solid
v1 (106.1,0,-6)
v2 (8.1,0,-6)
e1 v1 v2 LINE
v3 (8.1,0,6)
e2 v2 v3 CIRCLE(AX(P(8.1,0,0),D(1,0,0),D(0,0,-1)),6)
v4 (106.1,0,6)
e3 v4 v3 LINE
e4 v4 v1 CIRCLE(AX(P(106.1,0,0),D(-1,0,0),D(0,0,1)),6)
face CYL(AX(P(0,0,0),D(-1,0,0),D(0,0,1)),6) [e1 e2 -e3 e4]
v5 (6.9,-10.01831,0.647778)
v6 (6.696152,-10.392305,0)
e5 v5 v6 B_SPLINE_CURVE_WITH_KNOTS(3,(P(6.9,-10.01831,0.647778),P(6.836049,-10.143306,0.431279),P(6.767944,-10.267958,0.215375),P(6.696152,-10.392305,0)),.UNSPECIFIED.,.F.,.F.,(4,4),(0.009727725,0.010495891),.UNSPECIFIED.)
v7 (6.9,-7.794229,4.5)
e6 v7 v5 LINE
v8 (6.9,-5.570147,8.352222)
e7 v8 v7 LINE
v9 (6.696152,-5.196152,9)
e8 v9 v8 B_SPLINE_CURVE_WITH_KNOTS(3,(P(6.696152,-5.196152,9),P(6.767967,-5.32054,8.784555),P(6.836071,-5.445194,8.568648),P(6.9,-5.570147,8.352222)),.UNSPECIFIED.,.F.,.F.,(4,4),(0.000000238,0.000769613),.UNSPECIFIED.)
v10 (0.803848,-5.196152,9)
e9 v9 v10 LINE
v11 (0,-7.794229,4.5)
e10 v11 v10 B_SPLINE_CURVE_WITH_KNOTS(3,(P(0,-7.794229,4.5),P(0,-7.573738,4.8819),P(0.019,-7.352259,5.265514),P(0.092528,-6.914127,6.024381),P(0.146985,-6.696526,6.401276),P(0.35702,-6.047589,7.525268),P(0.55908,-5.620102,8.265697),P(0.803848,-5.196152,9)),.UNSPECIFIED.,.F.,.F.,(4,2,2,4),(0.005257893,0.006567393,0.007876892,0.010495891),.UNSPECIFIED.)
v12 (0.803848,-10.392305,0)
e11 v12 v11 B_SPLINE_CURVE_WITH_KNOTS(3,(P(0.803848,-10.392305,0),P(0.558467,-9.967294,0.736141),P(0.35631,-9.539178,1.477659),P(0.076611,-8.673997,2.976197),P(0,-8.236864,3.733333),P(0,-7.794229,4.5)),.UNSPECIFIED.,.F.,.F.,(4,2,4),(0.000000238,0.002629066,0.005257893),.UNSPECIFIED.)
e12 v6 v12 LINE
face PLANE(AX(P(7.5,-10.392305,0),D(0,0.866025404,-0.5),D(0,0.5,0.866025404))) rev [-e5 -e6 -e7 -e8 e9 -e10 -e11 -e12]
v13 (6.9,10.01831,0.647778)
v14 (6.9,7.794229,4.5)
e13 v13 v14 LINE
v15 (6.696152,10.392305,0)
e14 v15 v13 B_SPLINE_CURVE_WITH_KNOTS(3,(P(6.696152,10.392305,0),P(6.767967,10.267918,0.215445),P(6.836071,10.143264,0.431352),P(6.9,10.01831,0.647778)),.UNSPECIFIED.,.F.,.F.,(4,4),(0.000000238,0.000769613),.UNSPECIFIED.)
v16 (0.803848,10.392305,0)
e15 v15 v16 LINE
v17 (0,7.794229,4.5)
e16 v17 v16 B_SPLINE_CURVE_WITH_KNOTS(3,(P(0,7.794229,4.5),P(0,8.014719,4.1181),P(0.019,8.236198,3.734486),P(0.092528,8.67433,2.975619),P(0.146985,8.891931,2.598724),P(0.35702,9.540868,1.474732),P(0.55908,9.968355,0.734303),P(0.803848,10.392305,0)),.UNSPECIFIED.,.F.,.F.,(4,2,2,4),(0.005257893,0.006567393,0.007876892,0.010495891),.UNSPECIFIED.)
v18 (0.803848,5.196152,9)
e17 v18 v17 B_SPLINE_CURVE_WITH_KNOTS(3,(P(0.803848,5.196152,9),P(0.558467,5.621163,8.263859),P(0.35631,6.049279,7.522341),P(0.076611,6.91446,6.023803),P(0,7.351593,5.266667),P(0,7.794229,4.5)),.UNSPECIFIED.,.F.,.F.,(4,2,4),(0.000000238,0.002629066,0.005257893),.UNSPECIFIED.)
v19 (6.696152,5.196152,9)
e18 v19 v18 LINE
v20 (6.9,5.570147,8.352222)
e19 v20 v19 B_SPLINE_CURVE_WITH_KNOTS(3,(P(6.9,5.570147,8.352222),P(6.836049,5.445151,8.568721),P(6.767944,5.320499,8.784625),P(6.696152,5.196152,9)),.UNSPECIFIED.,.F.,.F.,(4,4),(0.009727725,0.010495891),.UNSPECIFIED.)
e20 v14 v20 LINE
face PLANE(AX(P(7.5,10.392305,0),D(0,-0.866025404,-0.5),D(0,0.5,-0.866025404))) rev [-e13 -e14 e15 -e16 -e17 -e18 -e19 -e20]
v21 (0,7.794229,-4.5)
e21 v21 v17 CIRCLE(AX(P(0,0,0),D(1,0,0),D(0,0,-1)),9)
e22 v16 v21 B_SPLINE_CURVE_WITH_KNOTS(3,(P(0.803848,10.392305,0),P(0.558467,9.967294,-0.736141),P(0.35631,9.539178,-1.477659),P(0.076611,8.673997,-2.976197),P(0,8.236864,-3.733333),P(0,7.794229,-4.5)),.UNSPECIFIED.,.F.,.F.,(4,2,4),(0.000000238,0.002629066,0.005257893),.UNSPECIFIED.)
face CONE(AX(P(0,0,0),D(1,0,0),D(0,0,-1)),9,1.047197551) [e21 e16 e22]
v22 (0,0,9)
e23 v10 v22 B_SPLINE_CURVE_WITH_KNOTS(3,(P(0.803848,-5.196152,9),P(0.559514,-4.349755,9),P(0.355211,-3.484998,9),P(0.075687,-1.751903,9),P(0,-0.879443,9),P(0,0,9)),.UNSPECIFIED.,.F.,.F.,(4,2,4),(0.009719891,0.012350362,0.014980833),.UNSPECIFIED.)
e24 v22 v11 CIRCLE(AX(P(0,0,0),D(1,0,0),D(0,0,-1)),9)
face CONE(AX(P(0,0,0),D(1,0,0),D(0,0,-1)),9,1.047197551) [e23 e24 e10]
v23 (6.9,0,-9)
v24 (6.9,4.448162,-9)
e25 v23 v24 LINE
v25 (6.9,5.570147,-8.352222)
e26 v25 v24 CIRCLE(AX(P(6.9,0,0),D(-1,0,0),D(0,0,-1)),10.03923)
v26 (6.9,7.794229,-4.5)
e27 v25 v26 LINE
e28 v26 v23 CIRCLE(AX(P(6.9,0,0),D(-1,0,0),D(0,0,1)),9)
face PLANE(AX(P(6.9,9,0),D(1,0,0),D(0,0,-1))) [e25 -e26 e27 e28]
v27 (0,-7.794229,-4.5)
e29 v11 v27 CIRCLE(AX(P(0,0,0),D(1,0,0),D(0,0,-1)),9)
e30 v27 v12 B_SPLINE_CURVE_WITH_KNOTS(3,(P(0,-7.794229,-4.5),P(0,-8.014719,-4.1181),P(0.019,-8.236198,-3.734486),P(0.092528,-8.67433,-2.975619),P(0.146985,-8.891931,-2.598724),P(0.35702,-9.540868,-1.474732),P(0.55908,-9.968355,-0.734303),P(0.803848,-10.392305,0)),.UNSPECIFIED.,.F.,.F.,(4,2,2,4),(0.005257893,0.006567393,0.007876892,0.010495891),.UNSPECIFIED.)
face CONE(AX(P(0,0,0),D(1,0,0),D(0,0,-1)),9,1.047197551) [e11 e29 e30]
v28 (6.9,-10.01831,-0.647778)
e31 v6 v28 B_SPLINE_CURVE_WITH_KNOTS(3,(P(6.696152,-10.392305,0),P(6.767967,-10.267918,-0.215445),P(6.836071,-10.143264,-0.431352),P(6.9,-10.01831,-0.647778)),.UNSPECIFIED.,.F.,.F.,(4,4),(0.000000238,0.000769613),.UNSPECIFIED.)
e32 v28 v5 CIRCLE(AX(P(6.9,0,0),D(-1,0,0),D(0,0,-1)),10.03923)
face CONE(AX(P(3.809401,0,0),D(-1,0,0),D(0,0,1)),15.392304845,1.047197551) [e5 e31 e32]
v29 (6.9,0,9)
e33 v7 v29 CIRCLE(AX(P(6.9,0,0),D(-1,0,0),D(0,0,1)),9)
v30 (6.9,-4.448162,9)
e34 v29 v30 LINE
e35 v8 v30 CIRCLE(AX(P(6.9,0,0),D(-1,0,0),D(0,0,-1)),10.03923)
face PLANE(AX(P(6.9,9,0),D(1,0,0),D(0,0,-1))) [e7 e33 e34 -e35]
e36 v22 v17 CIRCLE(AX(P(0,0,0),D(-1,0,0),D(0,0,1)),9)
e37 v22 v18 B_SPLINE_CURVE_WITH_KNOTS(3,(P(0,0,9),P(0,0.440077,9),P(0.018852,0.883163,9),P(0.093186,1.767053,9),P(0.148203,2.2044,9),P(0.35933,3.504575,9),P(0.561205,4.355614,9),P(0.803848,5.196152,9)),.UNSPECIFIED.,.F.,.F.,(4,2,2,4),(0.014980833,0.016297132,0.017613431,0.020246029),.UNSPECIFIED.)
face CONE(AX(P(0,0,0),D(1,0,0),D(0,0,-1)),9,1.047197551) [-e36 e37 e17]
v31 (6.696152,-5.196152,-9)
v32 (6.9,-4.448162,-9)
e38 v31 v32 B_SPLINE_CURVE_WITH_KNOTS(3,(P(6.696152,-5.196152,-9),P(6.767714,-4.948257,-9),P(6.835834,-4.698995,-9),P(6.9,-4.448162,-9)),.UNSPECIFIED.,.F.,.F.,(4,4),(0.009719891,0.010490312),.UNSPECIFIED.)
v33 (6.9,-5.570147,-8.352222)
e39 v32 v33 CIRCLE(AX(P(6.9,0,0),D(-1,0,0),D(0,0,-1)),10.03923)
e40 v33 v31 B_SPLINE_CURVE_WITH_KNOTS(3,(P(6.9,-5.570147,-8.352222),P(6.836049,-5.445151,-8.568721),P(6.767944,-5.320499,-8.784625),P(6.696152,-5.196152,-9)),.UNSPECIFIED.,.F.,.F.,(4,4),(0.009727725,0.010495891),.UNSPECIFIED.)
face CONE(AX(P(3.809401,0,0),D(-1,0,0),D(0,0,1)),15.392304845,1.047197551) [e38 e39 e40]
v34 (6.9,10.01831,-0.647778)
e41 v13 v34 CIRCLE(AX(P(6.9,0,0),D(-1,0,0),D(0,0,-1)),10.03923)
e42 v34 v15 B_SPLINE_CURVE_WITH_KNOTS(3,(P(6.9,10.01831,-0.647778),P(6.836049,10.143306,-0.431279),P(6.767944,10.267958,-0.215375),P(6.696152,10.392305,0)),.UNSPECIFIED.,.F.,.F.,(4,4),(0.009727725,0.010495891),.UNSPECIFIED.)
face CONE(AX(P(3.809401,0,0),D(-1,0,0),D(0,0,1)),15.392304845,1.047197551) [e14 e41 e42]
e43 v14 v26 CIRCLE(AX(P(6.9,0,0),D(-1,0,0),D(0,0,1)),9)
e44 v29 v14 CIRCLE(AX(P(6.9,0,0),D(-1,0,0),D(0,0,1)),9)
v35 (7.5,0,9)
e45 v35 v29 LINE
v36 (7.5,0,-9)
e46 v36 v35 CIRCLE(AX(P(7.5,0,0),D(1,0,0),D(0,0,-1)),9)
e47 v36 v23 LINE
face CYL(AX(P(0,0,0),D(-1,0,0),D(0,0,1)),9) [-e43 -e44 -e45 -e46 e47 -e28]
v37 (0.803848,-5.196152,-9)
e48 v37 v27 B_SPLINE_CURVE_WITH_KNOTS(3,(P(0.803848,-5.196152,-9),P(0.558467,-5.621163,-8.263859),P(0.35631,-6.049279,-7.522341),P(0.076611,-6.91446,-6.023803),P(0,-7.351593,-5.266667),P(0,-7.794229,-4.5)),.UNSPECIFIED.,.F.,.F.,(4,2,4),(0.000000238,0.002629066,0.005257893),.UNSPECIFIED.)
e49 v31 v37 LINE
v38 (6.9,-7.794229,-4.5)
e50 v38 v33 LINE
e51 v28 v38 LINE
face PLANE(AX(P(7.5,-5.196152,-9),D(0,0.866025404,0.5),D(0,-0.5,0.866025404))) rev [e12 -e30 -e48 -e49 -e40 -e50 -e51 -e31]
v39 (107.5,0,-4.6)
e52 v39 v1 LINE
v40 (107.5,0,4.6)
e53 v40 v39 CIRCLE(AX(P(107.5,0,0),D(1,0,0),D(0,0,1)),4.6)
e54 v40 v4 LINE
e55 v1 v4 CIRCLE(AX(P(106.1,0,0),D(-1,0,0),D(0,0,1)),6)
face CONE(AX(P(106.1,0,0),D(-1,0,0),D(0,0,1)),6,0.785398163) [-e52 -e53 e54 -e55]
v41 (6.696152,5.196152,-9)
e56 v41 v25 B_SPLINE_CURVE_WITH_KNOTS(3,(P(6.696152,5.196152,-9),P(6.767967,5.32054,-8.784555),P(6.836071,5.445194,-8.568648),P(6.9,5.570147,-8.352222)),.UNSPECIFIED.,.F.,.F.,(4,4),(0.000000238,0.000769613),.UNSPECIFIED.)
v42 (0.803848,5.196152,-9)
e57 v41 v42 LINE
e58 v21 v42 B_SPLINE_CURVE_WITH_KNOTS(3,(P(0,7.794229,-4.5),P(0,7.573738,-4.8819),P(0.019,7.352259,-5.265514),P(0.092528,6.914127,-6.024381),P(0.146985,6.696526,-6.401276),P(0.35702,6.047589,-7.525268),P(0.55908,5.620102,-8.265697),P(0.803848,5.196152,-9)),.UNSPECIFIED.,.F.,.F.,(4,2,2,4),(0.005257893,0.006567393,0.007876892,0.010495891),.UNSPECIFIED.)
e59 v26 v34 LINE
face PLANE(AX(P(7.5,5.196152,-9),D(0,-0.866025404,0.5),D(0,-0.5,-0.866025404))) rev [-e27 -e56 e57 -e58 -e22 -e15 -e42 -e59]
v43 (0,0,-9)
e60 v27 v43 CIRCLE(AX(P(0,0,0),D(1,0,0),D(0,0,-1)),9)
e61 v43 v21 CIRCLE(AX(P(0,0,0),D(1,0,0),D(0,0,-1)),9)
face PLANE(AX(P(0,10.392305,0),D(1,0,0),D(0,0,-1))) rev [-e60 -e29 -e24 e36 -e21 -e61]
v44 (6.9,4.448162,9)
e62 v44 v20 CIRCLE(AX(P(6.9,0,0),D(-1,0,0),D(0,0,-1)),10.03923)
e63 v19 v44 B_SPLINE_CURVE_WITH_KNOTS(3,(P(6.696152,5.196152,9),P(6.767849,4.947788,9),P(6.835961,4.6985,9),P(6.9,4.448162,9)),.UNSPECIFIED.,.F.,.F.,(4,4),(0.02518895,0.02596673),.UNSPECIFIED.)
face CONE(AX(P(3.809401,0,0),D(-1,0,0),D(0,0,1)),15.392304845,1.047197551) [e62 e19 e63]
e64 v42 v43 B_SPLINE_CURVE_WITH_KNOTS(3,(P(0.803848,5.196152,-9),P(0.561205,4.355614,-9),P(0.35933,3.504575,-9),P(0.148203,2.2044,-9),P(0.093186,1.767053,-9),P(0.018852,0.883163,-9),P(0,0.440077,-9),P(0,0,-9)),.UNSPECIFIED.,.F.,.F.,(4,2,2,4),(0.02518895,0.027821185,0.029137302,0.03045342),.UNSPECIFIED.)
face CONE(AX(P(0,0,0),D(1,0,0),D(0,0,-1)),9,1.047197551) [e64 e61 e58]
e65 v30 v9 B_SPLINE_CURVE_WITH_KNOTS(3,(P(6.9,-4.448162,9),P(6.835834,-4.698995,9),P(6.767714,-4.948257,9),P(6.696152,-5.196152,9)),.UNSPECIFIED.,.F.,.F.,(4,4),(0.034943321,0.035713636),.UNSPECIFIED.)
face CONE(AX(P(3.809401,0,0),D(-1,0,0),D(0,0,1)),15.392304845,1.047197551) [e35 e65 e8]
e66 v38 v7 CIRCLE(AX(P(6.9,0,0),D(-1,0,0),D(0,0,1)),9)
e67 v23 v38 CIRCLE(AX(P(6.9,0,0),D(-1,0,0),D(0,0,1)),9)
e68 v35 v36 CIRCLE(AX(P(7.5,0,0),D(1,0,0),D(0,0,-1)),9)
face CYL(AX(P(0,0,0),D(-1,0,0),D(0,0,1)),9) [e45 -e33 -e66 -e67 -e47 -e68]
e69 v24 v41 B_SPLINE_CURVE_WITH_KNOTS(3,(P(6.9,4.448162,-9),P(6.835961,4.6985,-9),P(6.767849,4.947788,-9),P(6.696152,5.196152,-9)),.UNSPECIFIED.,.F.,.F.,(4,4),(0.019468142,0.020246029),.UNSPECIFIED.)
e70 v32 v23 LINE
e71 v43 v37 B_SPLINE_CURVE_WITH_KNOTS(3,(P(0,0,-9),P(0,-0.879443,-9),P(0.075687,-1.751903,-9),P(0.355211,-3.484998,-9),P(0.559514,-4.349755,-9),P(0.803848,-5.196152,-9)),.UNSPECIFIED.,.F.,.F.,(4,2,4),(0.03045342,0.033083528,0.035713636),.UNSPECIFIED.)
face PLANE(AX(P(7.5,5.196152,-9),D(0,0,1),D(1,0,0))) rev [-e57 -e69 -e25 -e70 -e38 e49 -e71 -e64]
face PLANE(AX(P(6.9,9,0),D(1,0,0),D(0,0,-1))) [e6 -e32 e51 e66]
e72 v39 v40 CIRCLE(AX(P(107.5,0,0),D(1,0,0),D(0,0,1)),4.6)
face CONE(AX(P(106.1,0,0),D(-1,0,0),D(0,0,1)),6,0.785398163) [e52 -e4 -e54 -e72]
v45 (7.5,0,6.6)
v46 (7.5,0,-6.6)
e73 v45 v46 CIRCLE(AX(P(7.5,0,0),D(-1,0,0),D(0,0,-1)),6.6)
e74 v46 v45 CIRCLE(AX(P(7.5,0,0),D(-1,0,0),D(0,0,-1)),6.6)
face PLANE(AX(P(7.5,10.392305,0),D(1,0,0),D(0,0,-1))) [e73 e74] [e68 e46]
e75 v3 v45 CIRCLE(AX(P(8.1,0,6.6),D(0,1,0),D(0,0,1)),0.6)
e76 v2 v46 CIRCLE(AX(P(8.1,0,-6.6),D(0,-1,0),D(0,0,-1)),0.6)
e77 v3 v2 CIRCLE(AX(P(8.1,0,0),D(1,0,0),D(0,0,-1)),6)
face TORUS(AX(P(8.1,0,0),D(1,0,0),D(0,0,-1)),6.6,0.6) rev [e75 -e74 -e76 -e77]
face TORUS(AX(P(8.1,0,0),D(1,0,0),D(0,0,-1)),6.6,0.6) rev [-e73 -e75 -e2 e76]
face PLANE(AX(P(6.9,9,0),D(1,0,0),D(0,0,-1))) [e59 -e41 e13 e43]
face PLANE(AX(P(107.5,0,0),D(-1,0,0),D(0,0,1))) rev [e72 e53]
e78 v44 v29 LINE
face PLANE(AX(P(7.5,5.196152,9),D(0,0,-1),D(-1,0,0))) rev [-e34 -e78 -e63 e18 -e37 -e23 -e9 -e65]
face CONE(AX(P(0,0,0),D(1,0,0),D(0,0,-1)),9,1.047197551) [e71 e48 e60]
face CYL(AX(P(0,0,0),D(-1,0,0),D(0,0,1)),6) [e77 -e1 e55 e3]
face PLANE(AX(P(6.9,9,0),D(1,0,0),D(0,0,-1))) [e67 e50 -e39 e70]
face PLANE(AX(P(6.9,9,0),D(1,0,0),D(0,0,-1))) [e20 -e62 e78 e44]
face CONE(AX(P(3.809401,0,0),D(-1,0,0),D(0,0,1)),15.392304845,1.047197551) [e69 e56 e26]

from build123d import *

# Parameters (mm, degrees)
BASE_EXTRUDE_DEPTH = 7.5
SKETCH4_W          = 0.6
SKETCH4_H          = 11.392304845
CHAMFER_2_SIZE     = 1.4
FILLET_2_R         = 0.6


with BuildPart() as part:
    # Sketch1 → Base-extrude (new body)
    with BuildSketch(Plane(origin=(0, 0, 0), x_dir=(0, 0, -1), z_dir=(1, 0, 0))):
        Polygon((9, 5.196152423), (9, -5.196152423), (0, -10.392304845), (-9, -5.196152423), (-9, 5.196152423), (0, 10.392304845), align=None)
    extrude(amount=BASE_EXTRUDE_DEPTH)

    # Sketch2 → Boss-Revolve1 (revolve)
    with BuildSketch(Plane.XY, mode=Mode.PRIVATE) as boss_revolve1_sk:
        Polygon((0, 0), (107.5, 0), (107.5, 4.4845), (107.5, 6), (7.791693541, 6), (0, 6), align=None)
    revolve(boss_revolve1_sk.sketch.rotate(Axis((0, 0, 0), (1, 0, 0)), 90), axis=Axis((0, 0, 0), (1, 0, 0)))

    # Sketch3 → Cut-Revolve1 (revolve, cut)
    with BuildSketch(Plane.XY):
        Polygon((0, 9), (3.690598923, 15.392304845), (3.690598923, 20.392304845), (-10, 20.392304845), (-10, 9), align=None)
    revolve(axis=Axis((0, 0, 0), (1, 0, 0)), mode=Mode.SUBTRACT)

    # Sketch5 → Cut-Revolve2 (revolve, cut)
    with BuildSketch(Plane.XY):
        Polygon((7.5, 9), (3.809401077, 15.392304845), (3.809401077, 20.392304845), (13.809401077, 20.392304845), (13.809401077, 9), align=None)
    revolve(axis=Axis((0, 0, 0), (1, 0, 0)), mode=Mode.SUBTRACT)

    # Sketch4 → Cut-Revolve3 (revolve, cut)
    with BuildSketch(Plane.XY, mode=Mode.PRIVATE) as cut_revolve3_sk:
        with Locations((7.2, 14.696152423)):
            Rectangle(SKETCH4_W, SKETCH4_H)
    revolve(cut_revolve3_sk.sketch.rotate(Axis((0, 0, 0), (1, 0, 0)), 270), axis=Axis((0, 0, 0), (1, 0, 0)), mode=Mode.SUBTRACT)

    # Chamfer 2
    chamfer_2_edges = [part.edges().sort_by_distance(p)[0] for p in [
        (107.5, 0, -6),
    ]]
    chamfer(chamfer_2_edges, length=CHAMFER_2_SIZE)

    # Fillet 2
    fillet_2_edges = [part.edges().sort_by_distance(p)[0] for p in [
        (7.5, 0, -6),
    ]]
    fillet(fillet_2_edges, radius=FILLET_2_R)


solid = part.part
